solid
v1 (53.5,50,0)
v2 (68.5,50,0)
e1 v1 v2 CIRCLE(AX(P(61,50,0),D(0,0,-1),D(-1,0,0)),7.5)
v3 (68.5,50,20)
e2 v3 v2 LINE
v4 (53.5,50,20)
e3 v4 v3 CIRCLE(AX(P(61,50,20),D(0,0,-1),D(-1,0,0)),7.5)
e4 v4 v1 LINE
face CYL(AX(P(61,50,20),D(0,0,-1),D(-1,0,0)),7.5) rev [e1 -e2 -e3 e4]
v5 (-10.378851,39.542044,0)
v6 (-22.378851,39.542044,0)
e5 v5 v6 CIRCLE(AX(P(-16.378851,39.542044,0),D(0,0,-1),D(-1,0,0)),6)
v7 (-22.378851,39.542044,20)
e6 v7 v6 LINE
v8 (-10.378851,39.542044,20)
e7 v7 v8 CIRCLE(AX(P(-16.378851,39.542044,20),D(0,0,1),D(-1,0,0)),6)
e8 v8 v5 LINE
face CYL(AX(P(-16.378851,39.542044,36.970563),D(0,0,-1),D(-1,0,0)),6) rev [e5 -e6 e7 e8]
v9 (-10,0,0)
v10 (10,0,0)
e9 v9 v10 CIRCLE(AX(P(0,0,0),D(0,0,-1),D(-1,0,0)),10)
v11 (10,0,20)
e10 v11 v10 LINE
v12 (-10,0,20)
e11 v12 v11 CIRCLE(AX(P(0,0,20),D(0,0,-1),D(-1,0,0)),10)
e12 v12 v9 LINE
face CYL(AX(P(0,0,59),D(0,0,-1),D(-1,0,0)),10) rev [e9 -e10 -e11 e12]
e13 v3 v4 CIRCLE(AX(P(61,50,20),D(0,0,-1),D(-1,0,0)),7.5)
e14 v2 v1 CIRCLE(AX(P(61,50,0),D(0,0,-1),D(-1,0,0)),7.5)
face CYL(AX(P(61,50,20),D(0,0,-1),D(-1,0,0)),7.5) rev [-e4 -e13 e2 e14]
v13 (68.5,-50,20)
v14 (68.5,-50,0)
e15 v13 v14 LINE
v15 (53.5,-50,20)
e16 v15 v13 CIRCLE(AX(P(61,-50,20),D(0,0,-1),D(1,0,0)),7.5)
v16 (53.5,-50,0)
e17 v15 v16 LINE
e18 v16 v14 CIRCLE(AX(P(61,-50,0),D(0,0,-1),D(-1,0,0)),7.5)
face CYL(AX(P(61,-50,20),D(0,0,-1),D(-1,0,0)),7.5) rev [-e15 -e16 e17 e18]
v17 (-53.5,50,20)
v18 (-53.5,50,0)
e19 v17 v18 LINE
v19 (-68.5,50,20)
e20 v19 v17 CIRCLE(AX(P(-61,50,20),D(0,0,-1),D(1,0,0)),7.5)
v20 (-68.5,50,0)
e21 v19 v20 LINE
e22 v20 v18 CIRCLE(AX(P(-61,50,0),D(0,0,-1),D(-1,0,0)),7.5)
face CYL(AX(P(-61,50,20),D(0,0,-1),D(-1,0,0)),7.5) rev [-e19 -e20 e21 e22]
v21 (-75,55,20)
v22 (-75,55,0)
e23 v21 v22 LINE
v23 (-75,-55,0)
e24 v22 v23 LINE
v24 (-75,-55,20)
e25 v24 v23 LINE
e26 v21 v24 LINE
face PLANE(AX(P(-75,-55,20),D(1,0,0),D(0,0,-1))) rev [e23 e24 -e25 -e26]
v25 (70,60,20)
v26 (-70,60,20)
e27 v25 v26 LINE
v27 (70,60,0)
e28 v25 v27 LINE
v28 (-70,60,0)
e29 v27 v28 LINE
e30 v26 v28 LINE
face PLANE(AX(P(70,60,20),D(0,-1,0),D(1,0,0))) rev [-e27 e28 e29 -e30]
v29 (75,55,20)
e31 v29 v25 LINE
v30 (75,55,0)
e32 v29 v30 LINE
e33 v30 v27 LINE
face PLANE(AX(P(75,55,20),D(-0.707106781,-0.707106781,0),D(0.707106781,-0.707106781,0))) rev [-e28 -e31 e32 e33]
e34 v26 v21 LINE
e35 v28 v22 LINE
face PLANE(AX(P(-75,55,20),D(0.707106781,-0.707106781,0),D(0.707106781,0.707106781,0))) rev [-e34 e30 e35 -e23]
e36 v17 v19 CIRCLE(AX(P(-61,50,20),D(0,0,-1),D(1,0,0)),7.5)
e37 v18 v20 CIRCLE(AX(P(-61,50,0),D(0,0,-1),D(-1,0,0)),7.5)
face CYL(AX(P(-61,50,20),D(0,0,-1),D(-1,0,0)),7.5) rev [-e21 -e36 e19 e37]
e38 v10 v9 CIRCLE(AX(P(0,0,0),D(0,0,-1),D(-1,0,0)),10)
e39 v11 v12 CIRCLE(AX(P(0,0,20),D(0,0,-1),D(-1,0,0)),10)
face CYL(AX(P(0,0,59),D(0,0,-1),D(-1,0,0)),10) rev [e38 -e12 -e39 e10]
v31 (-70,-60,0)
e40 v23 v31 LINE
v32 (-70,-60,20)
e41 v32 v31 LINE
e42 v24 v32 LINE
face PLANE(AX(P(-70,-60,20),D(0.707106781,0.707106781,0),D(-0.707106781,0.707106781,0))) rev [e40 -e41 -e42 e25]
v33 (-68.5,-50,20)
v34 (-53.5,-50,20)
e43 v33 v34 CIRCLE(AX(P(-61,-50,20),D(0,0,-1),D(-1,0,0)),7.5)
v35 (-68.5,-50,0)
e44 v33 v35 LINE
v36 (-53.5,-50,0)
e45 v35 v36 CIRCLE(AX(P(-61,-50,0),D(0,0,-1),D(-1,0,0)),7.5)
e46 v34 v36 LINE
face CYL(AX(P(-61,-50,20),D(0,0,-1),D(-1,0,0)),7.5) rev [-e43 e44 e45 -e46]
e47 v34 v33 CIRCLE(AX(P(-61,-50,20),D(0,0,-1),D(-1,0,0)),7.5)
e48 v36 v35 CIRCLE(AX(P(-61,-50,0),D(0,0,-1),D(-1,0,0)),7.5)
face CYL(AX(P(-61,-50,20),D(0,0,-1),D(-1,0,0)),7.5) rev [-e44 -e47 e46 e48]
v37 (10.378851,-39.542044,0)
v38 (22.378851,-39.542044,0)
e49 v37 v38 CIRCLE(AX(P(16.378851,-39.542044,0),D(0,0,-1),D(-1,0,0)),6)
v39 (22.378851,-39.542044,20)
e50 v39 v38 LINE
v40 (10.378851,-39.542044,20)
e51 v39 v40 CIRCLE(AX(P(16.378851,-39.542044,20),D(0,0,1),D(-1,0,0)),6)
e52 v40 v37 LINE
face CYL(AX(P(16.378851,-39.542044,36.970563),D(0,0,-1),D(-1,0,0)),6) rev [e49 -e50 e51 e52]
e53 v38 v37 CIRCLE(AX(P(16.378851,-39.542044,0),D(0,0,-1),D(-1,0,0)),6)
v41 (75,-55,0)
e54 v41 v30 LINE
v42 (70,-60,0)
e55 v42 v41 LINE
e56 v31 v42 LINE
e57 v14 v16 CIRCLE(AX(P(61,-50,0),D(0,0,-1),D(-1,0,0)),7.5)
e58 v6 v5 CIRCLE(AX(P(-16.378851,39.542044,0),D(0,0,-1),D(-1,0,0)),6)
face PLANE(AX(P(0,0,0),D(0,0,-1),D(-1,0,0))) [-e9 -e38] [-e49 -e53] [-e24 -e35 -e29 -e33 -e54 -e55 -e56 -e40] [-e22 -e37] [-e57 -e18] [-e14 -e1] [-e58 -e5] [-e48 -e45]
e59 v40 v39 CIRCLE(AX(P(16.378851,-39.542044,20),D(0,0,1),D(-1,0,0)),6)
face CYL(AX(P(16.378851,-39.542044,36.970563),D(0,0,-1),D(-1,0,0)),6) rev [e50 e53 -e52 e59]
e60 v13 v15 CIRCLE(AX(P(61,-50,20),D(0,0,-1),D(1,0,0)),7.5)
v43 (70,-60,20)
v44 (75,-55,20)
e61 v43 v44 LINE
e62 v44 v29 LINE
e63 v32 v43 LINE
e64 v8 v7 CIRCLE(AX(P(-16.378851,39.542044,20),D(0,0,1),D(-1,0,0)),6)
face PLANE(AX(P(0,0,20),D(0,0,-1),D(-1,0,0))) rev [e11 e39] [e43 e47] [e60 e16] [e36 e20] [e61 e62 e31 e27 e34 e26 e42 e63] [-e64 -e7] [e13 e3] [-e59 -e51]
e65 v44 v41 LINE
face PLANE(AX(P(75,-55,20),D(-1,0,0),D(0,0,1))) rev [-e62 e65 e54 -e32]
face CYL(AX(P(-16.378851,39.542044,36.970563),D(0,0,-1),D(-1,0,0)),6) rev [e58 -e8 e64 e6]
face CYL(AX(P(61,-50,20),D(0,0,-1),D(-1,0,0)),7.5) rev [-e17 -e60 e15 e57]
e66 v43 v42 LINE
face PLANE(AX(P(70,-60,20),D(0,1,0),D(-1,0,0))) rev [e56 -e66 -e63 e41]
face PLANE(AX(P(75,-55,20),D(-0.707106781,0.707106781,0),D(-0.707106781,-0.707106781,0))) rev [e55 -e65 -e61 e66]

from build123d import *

# Parameters (mm, degrees)
BOSS_EXTRUDE1_DEPTH     = 20
CUT_EXTRUDE1_DEPTH      = 99.107084352
CUT_EXTRUDE1_DEPTH_BACK = 99.107084352
SKETCH3_R               = 7.5
SKETCH4_R               = 10
CUT_EXTRUDE2_DEPTH      = 59
CUT_EXTRUDE3_REACH      = 100.107
SKETCH5_R               = 6


with BuildPart() as part:
    # Sketch2 → Boss-Extrude1 (new body)
    with BuildSketch(Plane.XY):
        Polygon((75, -55), (70, -60), (-70, -60), (-75, -55), (-75, 55), (-70, 60), (70, 60), (75, 55), align=None)
    extrude(amount=BOSS_EXTRUDE1_DEPTH)

    # Sketch3 → Cut-Extrude1 (cut, two sides: drawn at the far end of the back side and taken through both)
    with BuildSketch(Plane(origin=(0, 0, 0), x_dir=(-1, 0, 0), z_dir=(0, 0, -1)).offset(-CUT_EXTRUDE1_DEPTH_BACK)):
        with Locations((61, -50)):
            Circle(SKETCH3_R)
        with Locations((61, 50)):
            Circle(SKETCH3_R)
        with Locations((-61, -50)):
            Circle(SKETCH3_R)
        with Locations((-61, 50)):
            Circle(SKETCH3_R)
    extrude(amount=CUT_EXTRUDE1_DEPTH + CUT_EXTRUDE1_DEPTH_BACK, mode=Mode.SUBTRACT)

    # Sketch4 → Cut-Extrude2 (cut)
    with BuildSketch(Plane(origin=(0, 0, 0), x_dir=(-1, 0, 0), z_dir=(0, 0, -1))):
        Circle(SKETCH4_R)
    extrude(amount=-CUT_EXTRUDE2_DEPTH, mode=Mode.SUBTRACT)

    # Sketch5 → Cut-Extrude3 (cut, up to next)
    with BuildSketch(Plane(origin=(0, 0, 0), x_dir=(-1, 0, 0), z_dir=(0, 0, -1)), mode=Mode.PRIVATE) as cut_extrude3_sk1:
        with Locations((-16.378850905, -39.542043991)):
            Circle(SKETCH5_R)
    cut_extrude3_tool1 = extrude(cut_extrude3_sk1.sketch, amount=-CUT_EXTRUDE3_REACH, mode=Mode.PRIVATE) & part.part
    # Sketch5 → Cut-Extrude3 (cut, up to next)
    with BuildSketch(Plane(origin=(0, 0, 0), x_dir=(-1, 0, 0), z_dir=(0, 0, -1)), mode=Mode.PRIVATE) as cut_extrude3_sk2:
        with Locations((16.378850905, 39.542043991)):
            Circle(SKETCH5_R)
    cut_extrude3_tool2 = extrude(cut_extrude3_sk2.sketch, amount=-CUT_EXTRUDE3_REACH, mode=Mode.PRIVATE) & part.part
    add(cut_extrude3_tool1.solids().sort_by_distance((16.378851, -39.542044, 0))[0], mode=Mode.SUBTRACT)
    add(cut_extrude3_tool2.solids().sort_by_distance((-16.378851, 39.542044, 0))[0], mode=Mode.SUBTRACT)


solid = part.part
